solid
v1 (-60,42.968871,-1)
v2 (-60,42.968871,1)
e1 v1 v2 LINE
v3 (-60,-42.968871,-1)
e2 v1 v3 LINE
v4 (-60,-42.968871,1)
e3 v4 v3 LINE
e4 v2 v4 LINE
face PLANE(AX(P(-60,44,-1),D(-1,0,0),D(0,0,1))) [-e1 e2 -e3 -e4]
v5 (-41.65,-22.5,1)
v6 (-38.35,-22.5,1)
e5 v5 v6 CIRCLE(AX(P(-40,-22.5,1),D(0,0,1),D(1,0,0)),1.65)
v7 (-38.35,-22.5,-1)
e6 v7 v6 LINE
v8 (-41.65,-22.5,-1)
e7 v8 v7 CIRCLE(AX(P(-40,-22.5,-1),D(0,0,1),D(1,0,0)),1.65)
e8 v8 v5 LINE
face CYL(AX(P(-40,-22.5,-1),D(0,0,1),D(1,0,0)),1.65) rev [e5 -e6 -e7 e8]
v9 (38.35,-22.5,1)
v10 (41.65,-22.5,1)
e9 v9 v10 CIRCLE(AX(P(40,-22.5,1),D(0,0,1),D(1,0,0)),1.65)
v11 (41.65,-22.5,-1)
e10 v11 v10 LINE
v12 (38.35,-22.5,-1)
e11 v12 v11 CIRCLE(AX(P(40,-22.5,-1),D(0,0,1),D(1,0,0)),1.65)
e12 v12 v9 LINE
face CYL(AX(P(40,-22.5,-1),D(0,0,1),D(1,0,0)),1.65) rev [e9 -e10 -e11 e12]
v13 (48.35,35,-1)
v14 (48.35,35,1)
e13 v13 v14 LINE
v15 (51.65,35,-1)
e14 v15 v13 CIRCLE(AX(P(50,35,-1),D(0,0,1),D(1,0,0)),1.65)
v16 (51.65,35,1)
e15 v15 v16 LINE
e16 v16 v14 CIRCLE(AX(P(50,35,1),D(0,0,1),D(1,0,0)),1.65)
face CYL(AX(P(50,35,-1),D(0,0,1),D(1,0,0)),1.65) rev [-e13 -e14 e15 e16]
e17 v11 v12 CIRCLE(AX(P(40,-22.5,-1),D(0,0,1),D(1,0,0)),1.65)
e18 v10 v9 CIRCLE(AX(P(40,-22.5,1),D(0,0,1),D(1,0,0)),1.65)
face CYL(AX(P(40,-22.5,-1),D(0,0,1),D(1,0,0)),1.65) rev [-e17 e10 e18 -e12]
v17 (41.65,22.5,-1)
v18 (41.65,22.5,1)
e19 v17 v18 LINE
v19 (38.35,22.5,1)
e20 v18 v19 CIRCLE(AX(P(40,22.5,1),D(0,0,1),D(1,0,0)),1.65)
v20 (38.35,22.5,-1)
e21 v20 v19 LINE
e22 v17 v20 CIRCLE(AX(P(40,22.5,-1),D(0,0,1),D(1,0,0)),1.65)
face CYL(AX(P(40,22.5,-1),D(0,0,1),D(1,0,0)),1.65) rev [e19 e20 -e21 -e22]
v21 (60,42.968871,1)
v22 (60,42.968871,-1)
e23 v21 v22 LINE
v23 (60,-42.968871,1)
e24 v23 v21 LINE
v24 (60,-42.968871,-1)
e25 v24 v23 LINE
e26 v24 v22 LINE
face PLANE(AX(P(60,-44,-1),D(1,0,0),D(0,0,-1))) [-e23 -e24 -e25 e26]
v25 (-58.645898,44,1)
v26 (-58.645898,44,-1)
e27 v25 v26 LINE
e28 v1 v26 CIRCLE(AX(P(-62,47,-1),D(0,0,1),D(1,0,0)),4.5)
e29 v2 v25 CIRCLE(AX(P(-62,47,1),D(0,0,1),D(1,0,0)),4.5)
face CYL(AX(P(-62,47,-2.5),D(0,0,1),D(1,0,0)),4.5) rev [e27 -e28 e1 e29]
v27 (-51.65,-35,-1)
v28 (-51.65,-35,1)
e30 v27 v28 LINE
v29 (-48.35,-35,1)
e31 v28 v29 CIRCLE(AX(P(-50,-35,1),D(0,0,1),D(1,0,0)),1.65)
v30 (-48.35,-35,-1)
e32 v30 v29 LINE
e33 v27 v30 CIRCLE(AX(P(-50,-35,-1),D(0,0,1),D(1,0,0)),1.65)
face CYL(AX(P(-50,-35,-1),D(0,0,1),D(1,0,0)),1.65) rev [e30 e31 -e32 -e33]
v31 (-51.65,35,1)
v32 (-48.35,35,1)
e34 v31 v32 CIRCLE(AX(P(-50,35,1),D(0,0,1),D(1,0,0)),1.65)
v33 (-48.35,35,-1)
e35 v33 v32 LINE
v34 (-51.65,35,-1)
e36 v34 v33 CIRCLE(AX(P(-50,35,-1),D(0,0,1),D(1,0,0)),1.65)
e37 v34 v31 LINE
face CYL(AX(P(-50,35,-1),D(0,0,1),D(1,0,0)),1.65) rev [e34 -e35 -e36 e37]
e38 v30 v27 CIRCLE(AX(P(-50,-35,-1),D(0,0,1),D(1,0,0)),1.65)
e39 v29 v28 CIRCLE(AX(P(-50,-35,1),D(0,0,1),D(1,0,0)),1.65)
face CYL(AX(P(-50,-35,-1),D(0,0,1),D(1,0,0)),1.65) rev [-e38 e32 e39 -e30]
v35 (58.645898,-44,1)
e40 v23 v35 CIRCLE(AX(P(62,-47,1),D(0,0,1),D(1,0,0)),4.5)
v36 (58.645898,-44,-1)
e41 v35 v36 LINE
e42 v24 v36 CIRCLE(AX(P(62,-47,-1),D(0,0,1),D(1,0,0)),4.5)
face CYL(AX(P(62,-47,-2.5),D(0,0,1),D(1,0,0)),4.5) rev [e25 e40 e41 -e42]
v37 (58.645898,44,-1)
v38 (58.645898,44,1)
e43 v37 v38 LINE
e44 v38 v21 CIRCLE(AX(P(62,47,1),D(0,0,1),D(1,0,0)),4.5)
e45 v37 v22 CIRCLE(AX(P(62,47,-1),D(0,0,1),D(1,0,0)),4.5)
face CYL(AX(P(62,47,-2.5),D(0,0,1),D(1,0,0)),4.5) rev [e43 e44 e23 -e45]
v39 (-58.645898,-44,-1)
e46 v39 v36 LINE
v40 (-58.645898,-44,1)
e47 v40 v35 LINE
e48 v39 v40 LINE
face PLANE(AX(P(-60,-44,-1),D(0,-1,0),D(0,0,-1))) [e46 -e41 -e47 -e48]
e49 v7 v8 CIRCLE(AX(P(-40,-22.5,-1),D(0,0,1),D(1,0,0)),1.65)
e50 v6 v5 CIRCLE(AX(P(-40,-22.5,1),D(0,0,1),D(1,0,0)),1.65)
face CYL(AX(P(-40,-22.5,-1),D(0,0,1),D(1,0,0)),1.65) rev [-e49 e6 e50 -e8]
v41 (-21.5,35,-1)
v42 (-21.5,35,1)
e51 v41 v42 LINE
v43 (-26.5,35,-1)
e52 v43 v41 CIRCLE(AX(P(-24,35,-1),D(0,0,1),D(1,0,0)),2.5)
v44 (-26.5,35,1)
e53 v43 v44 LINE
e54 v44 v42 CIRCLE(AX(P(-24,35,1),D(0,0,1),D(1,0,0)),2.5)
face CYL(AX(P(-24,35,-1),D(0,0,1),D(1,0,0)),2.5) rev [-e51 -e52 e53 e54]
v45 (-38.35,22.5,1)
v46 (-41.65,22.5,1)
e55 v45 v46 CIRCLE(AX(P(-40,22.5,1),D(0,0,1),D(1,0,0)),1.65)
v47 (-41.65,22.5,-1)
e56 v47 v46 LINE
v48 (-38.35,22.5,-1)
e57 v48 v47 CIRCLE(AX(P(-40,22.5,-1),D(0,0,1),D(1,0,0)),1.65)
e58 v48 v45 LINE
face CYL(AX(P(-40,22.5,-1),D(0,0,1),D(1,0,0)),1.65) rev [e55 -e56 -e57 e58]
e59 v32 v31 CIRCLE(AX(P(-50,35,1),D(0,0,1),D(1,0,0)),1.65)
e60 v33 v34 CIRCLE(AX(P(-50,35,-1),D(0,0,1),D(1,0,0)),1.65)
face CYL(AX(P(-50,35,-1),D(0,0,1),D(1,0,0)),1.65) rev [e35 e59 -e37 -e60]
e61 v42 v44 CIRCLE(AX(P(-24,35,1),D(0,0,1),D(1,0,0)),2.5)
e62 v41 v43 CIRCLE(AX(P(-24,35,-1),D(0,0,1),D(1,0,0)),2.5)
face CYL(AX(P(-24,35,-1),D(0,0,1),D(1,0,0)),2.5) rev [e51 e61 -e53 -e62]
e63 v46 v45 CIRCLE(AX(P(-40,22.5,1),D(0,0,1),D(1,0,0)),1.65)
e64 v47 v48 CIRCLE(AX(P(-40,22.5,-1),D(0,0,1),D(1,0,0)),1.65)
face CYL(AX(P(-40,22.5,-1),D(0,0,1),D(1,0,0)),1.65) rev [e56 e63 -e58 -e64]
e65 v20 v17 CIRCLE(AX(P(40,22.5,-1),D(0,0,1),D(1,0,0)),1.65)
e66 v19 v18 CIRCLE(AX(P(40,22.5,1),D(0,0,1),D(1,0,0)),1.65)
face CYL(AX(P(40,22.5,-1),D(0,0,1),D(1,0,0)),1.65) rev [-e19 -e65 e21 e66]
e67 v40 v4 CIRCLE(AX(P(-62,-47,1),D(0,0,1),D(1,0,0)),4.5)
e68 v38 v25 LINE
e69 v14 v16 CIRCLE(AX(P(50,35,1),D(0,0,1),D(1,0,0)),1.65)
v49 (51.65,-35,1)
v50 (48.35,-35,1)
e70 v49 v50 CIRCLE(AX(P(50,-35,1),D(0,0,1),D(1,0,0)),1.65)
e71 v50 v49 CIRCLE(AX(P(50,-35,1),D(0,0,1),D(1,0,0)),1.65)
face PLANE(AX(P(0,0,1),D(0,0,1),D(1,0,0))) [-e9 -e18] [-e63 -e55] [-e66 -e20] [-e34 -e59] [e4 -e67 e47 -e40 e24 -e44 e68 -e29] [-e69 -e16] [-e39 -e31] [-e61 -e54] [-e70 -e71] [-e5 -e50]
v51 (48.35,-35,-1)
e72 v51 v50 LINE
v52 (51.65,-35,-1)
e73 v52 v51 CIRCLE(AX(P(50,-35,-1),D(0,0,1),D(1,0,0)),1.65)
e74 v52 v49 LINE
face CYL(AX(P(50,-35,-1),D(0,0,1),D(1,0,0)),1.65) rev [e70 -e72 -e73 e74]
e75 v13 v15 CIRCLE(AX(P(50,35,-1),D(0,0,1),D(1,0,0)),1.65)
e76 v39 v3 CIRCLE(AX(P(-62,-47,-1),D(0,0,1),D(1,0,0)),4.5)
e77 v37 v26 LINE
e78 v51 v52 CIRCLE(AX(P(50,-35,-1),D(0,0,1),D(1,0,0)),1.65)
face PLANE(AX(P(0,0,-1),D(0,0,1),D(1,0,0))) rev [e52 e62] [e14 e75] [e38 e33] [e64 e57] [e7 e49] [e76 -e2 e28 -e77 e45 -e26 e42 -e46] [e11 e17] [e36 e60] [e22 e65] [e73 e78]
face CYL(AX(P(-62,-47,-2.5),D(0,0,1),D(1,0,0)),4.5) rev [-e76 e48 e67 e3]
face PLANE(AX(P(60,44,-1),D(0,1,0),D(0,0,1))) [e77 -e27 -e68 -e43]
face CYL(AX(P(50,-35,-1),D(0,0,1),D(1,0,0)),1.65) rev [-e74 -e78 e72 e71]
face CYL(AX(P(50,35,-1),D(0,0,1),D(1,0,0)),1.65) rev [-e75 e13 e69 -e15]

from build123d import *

# Parameters (mm, degrees)
SKETCH_1_W          = 120
SKETCH_1_H          = 88
SKETCH_1_R          = 1.65
SKETCH_1_R_2        = 2.5
EXTRUDE_1_DEPTH     = 1
SKETCH_2_R          = 4.5
CUT_EXTRUDE_1_DEPTH = 2.5


with BuildPart() as part:
    # 草图1 → 凸台-拉伸1 (new, symmetric)
    with BuildSketch(Plane.XY):
        Rectangle(SKETCH_1_W, SKETCH_1_H)
        with Locations((-40, -22.5)):
            Circle(SKETCH_1_R, mode=Mode.SUBTRACT)
        with Locations((-40, 22.5)):
            Circle(SKETCH_1_R, mode=Mode.SUBTRACT)
        with Locations((40, -22.5)):
            Circle(SKETCH_1_R, mode=Mode.SUBTRACT)
        with Locations((40, 22.5)):
            Circle(SKETCH_1_R, mode=Mode.SUBTRACT)
        with Locations((-50, -35)):
            Circle(SKETCH_1_R, mode=Mode.SUBTRACT)
        with Locations((-50, 35)):
            Circle(SKETCH_1_R, mode=Mode.SUBTRACT)
        with Locations((50, -35)):
            Circle(SKETCH_1_R, mode=Mode.SUBTRACT)
        with Locations((50, 35)):
            Circle(SKETCH_1_R, mode=Mode.SUBTRACT)
        with Locations((-24, 35)):
            Circle(SKETCH_1_R_2, mode=Mode.SUBTRACT)
    extrude(amount=EXTRUDE_1_DEPTH, both=True)

    # 草图2 → 切除-拉伸1 (cut, symmetric)
    with BuildSketch(Plane.XY):
        with Locations((-62, -47)):
            Circle(SKETCH_2_R)
        with Locations((-62, 47)):
            Circle(SKETCH_2_R)
        with Locations((62, -47)):
            Circle(SKETCH_2_R)
        with Locations((62, 47)):
            Circle(SKETCH_2_R)
    extrude(amount=CUT_EXTRUDE_1_DEPTH, both=True, mode=Mode.SUBTRACT)


solid = part.part
